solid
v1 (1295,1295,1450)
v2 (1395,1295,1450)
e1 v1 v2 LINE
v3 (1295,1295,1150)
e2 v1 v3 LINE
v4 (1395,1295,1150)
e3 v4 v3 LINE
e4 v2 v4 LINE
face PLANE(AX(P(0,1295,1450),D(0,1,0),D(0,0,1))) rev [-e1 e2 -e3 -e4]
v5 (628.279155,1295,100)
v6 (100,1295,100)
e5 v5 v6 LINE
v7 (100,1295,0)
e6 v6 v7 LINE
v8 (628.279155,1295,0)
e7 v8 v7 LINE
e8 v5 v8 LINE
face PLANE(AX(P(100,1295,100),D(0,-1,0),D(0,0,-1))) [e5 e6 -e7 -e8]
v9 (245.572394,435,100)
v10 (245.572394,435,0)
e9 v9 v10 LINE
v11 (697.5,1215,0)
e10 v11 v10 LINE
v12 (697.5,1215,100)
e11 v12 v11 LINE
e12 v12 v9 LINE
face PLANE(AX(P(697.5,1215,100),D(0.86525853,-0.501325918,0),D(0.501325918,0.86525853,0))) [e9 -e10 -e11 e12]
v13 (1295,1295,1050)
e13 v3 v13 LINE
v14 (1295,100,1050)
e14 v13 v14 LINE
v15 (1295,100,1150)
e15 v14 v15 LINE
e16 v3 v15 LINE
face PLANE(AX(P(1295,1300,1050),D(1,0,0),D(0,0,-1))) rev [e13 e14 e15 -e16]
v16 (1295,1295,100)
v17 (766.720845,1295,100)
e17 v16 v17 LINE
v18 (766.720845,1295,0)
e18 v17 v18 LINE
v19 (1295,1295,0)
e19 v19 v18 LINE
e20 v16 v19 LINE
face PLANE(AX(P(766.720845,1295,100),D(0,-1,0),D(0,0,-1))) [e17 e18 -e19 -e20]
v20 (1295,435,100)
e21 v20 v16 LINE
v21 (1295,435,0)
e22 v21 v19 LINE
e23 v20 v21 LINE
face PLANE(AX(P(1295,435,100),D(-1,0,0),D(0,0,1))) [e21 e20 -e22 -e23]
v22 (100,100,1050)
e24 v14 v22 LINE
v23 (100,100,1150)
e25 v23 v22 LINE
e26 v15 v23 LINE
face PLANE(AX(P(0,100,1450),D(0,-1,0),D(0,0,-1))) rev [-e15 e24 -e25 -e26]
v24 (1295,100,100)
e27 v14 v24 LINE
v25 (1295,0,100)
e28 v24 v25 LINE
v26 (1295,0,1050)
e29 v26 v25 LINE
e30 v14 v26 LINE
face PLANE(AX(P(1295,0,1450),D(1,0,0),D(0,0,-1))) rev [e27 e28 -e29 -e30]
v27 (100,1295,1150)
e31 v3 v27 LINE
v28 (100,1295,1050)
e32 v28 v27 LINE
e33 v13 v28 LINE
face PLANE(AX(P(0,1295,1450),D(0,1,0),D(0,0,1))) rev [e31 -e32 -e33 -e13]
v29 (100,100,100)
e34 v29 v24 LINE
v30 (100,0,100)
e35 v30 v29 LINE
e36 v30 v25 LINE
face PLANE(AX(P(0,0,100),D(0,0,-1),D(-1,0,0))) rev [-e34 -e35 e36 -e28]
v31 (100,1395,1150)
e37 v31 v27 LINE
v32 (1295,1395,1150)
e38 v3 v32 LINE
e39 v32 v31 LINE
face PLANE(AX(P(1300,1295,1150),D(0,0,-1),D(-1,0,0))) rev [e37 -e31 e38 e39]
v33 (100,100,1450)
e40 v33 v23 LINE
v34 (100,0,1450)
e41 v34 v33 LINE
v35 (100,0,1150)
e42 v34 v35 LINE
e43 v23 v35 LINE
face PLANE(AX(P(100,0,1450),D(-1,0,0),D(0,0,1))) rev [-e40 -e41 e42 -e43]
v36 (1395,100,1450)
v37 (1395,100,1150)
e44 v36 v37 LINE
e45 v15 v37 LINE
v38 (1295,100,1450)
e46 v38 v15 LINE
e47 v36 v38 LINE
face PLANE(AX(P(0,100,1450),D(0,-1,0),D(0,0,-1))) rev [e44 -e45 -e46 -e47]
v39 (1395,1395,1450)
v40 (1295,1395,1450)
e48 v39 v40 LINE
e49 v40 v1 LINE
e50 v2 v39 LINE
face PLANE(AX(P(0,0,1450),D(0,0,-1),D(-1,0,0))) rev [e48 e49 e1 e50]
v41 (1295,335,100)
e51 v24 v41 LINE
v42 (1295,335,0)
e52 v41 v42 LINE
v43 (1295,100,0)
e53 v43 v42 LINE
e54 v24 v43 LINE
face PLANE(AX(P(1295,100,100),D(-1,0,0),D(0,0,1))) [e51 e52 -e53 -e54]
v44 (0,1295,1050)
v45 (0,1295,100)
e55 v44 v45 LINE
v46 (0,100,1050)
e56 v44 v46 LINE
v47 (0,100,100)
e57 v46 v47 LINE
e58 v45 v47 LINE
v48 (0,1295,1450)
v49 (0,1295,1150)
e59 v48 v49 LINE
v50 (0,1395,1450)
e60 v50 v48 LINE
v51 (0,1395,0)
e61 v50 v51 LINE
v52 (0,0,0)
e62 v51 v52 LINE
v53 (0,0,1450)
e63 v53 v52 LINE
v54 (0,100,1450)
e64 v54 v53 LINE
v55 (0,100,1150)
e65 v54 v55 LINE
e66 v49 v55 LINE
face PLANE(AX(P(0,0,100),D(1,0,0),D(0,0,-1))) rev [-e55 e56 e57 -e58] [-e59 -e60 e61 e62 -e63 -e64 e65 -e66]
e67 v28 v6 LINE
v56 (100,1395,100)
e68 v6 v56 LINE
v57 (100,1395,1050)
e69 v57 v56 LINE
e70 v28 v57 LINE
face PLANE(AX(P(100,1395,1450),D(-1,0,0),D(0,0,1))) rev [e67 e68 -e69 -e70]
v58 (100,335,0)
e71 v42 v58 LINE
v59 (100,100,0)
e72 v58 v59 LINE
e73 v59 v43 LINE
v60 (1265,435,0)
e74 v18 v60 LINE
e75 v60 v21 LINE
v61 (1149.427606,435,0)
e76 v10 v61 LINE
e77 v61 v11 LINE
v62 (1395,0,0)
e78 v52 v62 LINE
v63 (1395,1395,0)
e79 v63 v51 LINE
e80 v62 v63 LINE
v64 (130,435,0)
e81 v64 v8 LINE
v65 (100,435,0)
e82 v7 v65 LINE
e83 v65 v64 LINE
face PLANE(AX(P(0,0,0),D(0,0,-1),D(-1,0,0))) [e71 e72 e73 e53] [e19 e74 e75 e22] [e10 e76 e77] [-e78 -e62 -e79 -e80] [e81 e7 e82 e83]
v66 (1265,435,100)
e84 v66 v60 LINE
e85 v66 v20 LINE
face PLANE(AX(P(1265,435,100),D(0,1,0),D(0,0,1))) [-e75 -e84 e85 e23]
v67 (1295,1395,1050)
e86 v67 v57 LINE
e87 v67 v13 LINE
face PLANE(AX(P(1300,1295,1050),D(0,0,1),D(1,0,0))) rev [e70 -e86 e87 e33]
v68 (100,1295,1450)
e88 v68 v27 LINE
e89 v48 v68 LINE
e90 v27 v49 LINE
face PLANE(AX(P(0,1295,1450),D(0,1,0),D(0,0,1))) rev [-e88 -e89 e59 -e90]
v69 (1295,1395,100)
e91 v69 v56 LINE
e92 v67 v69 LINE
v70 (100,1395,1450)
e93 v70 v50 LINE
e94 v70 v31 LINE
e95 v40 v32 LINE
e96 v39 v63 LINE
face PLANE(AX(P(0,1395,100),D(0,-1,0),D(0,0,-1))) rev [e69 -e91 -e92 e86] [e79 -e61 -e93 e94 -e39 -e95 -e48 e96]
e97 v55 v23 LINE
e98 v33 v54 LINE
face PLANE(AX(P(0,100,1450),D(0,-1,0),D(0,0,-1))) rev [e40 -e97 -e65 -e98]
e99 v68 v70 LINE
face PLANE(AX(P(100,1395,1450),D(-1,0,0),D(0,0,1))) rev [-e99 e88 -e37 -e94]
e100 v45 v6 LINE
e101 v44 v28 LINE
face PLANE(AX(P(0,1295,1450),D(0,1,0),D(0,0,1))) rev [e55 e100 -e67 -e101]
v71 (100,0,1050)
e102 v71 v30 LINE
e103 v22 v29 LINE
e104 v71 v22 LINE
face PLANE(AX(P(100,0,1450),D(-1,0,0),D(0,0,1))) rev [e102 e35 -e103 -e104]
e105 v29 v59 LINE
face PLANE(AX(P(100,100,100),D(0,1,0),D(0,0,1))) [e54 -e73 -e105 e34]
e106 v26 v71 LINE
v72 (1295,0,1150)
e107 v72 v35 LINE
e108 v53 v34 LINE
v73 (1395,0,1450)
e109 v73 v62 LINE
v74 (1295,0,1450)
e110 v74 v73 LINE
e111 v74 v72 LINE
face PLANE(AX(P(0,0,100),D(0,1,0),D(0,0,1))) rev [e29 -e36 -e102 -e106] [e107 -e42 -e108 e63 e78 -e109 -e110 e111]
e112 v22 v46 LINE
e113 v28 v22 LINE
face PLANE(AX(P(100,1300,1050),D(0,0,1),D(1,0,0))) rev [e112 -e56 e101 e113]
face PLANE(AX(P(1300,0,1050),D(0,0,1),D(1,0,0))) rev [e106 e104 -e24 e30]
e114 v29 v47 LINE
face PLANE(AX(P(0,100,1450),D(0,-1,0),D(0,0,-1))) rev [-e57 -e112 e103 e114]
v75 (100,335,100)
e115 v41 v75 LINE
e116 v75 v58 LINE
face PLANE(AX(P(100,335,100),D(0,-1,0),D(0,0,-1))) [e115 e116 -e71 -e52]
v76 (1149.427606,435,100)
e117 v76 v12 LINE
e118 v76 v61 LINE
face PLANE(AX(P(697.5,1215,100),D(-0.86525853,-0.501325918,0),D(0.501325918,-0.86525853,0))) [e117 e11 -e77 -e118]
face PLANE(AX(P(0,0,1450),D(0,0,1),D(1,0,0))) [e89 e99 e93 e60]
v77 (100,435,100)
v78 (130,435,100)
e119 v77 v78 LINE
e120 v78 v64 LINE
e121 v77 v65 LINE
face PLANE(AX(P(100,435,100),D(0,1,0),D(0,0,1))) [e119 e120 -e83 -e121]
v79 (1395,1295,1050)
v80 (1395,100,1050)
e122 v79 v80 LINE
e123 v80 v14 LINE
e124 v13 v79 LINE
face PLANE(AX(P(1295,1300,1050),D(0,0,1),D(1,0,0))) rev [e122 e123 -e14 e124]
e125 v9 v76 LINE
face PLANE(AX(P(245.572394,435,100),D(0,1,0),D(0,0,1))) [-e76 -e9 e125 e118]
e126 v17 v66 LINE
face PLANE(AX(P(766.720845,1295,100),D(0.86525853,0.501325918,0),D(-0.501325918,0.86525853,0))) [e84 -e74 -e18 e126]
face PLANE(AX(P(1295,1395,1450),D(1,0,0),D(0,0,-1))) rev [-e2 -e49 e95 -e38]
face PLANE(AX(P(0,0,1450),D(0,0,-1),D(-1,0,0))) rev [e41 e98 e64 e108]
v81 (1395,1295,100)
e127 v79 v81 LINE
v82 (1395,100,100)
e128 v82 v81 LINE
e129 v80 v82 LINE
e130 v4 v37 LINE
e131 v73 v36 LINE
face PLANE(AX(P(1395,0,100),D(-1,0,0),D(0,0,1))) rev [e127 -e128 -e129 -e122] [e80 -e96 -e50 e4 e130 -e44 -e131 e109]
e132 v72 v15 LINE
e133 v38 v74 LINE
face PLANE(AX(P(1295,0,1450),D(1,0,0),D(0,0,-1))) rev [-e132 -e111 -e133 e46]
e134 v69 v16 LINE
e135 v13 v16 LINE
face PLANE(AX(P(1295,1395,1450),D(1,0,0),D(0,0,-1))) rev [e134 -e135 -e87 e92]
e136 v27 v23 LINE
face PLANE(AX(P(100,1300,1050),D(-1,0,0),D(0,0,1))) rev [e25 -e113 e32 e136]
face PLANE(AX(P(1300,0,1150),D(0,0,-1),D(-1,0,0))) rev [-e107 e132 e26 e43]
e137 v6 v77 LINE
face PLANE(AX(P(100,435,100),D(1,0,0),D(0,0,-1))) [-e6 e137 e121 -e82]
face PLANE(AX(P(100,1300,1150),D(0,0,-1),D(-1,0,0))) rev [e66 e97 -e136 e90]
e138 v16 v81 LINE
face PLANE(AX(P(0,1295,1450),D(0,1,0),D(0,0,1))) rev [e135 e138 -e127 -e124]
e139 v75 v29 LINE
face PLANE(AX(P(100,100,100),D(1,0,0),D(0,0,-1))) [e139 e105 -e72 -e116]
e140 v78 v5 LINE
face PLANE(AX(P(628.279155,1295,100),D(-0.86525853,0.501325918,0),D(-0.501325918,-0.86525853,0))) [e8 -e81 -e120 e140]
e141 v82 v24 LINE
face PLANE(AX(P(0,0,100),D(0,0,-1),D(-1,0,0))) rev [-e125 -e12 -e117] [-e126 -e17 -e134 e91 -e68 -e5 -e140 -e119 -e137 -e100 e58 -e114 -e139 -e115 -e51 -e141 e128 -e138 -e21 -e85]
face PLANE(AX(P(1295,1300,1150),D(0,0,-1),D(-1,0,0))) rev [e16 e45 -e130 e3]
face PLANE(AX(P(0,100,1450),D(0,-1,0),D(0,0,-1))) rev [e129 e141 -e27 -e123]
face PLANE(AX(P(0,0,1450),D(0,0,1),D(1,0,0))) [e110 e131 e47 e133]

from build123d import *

# Parameters (mm, degrees)
SKETCH1_W           = 1395
SKETCH1_H           = 1395
SKETCH1_W_2         = 1195
SKETCH1_H_2         = 235
BOSS_EXTRUDE1_DEPTH = 100
SKETCH2_W           = 100
SKETCH2_H           = 100
BOSS_EXTRUDE2_DEPTH = 1350
SKETCH3_W           = 100
SKETCH3_H           = 100
BOSS_EXTRUDE3_DEPTH = 1200
SKETCH4_W           = 100
SKETCH4_H           = 100
BOSS_EXTRUDE4_DEPTH = 1200


with BuildPart() as part:
    # Sketch1 → Boss-Extrude1 (new body)
    with BuildSketch(Plane.XY):
        with Locations((697.5, 697.5)):
            Rectangle(SKETCH1_W, SKETCH1_H)
        with Locations((697.5, 217.5)):
            Rectangle(SKETCH1_W_2, SKETCH1_H_2, mode=Mode.SUBTRACT)
        Polygon((100, 1295), (628.279155036, 1295), (130, 435), (100, 435), align=None, mode=Mode.SUBTRACT)
        Polygon((766.720844964, 1295), (1265, 435), (1295, 435), (1295, 1295), align=None, mode=Mode.SUBTRACT)
        Polygon((697.5, 1215), (1149.42760573, 435), (245.57239427, 435), align=None, mode=Mode.SUBTRACT)
    extrude(amount=BOSS_EXTRUDE1_DEPTH)

    # Sketch2 → Boss-Extrude2 (add)
    with BuildSketch(Plane.XY.offset(100)):
        with Locations((50, 1345)):
            Rectangle(SKETCH2_W, SKETCH2_H)
        with Locations((1345, 1345)):
            Rectangle(SKETCH2_W, SKETCH2_H)
        with Locations((50, 50)):
            Rectangle(SKETCH2_W, SKETCH2_H)
        with Locations((1345, 50)):
            Rectangle(SKETCH2_W, SKETCH2_H)
    extrude(amount=BOSS_EXTRUDE2_DEPTH)

    # Sketch3 → Boss-Extrude3 (add)
    with BuildSketch(Plane(origin=(100, 0, 0), x_dir=(0, 0, -1), z_dir=(1, 0, 0))):
        with Locations((-1100, 50)):
            Rectangle(SKETCH3_W, SKETCH3_H)
        with Locations((-1100, 1345)):
            Rectangle(SKETCH3_W, SKETCH3_H)
    extrude(amount=BOSS_EXTRUDE3_DEPTH)

    # Sketch4 → Boss-Extrude4 (add)
    with BuildSketch(Plane(origin=(0, 100, 0), x_dir=(1, 0, 0), z_dir=(0, 1, 0))):
        with Locations((50, -1100)):
            Rectangle(SKETCH4_W, SKETCH4_H)
        with Locations((1345, -1100)):
            Rectangle(SKETCH4_W, SKETCH4_H)
    extrude(amount=BOSS_EXTRUDE4_DEPTH)


solid = part.part
